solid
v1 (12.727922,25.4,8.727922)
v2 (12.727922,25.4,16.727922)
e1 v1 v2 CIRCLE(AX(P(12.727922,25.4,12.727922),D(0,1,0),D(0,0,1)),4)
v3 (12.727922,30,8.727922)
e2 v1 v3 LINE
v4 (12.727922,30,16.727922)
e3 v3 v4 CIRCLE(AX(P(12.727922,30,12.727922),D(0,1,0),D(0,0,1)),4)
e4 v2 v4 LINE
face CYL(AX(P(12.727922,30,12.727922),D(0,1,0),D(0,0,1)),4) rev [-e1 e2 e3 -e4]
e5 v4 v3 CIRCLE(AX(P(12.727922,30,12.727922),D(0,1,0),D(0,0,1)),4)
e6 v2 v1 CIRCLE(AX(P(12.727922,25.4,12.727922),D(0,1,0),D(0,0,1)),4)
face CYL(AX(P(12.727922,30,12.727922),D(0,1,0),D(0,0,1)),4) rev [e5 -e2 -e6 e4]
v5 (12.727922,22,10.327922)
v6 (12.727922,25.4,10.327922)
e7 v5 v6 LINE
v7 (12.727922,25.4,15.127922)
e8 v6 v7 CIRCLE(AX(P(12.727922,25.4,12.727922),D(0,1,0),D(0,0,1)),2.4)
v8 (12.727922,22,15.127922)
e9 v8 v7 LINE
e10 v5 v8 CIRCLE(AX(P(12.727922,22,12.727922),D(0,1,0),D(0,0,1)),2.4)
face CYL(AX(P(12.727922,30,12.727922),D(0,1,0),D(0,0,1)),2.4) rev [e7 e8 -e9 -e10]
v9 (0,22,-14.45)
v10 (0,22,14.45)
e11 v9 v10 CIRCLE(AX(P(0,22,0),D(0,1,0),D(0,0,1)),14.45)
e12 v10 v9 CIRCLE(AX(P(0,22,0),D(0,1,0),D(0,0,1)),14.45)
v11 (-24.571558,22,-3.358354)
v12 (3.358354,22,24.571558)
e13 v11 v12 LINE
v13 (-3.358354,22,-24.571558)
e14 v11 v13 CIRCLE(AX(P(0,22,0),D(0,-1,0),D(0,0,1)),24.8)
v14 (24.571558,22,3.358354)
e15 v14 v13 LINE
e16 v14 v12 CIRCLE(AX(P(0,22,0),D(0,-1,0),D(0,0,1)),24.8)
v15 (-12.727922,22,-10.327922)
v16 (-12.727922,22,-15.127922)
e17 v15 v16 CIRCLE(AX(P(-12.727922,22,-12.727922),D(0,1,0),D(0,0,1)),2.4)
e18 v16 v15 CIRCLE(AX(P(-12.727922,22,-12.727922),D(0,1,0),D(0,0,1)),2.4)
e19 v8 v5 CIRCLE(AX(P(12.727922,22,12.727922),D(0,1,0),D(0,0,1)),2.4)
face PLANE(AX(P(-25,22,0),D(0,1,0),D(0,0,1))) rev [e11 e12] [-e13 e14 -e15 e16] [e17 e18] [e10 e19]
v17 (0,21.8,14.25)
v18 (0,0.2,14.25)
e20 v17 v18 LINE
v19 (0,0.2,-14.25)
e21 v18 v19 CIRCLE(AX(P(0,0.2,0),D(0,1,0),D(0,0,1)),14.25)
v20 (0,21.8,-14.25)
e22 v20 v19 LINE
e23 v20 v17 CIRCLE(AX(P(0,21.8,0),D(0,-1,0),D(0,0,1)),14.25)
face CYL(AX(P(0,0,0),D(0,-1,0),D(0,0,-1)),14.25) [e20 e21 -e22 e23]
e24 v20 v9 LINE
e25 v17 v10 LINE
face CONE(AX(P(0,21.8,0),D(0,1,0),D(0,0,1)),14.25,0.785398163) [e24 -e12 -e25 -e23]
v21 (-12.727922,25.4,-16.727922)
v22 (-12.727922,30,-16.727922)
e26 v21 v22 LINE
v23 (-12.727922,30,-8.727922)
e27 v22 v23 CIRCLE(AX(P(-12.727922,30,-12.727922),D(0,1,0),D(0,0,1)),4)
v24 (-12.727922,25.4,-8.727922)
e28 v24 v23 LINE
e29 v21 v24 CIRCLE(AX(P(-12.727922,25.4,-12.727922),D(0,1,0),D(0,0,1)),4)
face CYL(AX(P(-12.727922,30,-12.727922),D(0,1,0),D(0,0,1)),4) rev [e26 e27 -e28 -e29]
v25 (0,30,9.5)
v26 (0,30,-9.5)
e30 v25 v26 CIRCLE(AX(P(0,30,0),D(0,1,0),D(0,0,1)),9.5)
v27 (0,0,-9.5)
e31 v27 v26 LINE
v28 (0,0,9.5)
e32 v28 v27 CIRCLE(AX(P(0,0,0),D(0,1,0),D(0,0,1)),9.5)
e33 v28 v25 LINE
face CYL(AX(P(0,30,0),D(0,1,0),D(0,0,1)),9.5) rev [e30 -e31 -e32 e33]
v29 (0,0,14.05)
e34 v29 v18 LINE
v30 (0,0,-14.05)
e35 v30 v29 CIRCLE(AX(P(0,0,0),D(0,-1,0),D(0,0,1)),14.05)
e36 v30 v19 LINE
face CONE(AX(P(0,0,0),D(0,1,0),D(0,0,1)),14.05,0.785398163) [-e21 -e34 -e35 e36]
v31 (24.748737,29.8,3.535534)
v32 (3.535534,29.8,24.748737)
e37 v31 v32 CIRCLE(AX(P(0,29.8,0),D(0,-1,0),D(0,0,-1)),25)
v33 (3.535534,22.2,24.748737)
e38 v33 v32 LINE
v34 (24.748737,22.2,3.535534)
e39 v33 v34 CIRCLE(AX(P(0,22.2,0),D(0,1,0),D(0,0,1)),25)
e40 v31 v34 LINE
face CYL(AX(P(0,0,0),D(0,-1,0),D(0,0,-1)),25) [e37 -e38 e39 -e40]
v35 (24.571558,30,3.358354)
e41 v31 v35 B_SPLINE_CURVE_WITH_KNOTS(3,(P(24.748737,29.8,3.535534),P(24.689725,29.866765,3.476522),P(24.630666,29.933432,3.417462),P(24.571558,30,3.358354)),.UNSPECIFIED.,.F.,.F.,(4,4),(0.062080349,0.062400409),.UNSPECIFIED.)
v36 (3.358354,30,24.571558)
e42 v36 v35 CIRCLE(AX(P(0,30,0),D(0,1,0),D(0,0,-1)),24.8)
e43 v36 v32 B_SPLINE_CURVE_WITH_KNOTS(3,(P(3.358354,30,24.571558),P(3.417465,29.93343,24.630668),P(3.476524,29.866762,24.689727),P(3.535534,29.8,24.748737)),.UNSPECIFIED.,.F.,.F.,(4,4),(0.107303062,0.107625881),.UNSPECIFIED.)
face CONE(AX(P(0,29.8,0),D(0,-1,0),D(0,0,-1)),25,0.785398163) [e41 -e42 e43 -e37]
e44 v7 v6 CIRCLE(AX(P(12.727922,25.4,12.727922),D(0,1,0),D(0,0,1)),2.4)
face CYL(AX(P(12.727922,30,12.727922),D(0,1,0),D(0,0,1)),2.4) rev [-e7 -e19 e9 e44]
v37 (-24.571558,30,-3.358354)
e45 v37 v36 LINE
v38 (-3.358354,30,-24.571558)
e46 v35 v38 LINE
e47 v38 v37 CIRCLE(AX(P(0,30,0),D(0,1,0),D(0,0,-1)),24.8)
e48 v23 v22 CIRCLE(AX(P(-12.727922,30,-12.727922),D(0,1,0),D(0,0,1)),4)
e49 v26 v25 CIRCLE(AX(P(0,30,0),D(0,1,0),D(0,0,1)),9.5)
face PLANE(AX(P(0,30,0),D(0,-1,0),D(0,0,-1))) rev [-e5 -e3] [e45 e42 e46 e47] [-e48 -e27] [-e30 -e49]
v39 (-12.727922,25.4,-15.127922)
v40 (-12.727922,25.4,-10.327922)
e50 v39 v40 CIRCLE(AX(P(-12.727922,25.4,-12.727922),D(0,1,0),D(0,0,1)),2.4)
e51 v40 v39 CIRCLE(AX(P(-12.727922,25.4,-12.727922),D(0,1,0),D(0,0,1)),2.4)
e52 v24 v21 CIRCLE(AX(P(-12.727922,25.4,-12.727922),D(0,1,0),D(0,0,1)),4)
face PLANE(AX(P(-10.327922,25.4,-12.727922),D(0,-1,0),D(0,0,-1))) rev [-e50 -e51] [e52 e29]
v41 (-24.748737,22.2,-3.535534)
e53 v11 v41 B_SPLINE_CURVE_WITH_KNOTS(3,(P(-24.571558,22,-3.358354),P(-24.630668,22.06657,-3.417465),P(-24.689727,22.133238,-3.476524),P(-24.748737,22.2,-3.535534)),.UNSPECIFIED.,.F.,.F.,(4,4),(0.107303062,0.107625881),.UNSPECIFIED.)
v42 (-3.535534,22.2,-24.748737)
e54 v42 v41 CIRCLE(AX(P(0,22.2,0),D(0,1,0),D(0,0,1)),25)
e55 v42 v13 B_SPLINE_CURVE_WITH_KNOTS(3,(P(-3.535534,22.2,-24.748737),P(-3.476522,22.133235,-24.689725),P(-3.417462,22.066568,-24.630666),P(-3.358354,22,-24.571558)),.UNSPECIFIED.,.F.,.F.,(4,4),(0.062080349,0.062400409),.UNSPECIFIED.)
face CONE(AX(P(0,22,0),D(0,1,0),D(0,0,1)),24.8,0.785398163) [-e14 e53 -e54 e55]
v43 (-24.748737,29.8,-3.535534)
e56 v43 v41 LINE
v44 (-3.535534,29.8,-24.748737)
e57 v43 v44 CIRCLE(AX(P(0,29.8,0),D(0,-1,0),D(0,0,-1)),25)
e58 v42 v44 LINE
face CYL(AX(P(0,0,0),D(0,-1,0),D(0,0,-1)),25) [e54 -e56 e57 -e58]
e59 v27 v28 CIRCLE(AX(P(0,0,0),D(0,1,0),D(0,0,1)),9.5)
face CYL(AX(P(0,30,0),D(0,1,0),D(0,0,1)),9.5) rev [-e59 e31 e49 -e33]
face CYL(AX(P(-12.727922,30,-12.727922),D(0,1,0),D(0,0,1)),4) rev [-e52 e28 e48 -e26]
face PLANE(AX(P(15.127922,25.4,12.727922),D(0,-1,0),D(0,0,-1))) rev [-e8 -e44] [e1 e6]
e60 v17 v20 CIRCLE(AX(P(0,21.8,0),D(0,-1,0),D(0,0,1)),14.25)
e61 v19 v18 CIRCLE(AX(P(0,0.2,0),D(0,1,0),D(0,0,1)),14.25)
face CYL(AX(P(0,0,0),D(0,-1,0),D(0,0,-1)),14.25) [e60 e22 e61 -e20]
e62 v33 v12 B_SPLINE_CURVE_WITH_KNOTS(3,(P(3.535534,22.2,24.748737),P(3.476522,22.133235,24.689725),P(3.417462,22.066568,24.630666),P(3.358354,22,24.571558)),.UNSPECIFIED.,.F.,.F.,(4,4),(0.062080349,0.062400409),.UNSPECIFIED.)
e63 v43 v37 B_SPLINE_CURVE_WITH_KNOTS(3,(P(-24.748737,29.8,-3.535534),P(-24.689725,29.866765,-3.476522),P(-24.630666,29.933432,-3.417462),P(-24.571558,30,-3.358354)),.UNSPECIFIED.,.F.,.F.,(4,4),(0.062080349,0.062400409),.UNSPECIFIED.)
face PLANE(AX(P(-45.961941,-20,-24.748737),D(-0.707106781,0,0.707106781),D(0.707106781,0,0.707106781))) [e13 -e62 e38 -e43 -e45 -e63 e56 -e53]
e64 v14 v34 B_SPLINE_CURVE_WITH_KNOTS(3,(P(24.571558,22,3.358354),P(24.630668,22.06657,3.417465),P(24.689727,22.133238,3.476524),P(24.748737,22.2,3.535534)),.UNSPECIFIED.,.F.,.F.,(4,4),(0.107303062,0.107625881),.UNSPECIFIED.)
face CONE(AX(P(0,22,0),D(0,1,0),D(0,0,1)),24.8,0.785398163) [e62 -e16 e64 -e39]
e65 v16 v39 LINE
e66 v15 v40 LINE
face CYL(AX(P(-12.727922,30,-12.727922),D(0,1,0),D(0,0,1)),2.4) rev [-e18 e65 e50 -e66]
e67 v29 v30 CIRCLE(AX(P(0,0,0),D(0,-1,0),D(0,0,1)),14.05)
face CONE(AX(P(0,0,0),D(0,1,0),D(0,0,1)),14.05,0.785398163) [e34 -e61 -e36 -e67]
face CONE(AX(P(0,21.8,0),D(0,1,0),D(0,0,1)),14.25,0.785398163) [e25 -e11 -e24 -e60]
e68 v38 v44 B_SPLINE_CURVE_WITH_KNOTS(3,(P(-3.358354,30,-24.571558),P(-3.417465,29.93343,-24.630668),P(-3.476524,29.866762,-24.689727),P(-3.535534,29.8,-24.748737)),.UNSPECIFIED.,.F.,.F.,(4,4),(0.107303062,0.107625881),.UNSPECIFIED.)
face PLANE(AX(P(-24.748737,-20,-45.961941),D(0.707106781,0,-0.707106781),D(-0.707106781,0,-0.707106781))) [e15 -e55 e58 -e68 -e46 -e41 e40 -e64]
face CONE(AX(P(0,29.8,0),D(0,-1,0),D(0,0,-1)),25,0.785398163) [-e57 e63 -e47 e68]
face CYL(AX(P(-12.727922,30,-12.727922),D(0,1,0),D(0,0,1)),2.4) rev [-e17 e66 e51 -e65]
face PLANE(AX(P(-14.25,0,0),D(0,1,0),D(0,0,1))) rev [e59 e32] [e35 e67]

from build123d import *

# Parameters (mm, degrees)
G1_2_TAPPED_HOLE1_D                               = 19
HOLE_SIZE_BASED_ON_SOCKET_HEAD_CAP_SC_D           = 4.8
HOLE_SIZE_BASED_ON_SOCKET_HEAD_CAP_SC_CBORE_D     = 8
HOLE_SIZE_BASED_ON_SOCKET_HEAD_CAP_SC_CBORE_DEPTH = 4.6
CHAMFER1_SIZE                                     = 0.2
CHAMFER2_SIZE                                     = 0.2
SKETCH7_OUTSIDE_W                                 = 67.362
SKETCH7_OUTSIDE_H                                 = 67.362
CUT_EXTRUDE1_DEPTH                                = 50


with BuildPart() as part:
    # Sketch2 → Revolve1 (revolve)
    with BuildSketch(Plane.XY, mode=Mode.PRIVATE) as revolve1_sk:
        Polygon((0, 30), (-25, 30), (-25, 22), (-14.25, 22), (-14.25, 0), (0, 0), align=None)
    revolve(revolve1_sk.sketch.rotate(Axis((0, 0, 0), (0, 1, 0)), 270), axis=Axis((0, 0, 0), (0, 1, 0)))

    # G1/2 Tapped Hole1 (through all)
    with Locations(Plane.ZX.offset(30)):
        with Locations((0, 0)):
            Hole(G1_2_TAPPED_HOLE1_D / 2)

    # Hole Size (% based on) Socket Head Cap Screw Type 1 (through all)
    with Locations(Plane(origin=(-12.727922061, 30, -12.727922061), x_dir=(0, 0, 1), z_dir=(0, 1, 0))):
        with Locations((0, 0), (25.455844122, 25.455844122)):
            CounterBoreHole(HOLE_SIZE_BASED_ON_SOCKET_HEAD_CAP_SC_D / 2, HOLE_SIZE_BASED_ON_SOCKET_HEAD_CAP_SC_CBORE_D / 2, HOLE_SIZE_BASED_ON_SOCKET_HEAD_CAP_SC_CBORE_DEPTH)

    # Chamfer1
    chamfer1_edges = [part.edges().sort_by_distance(p)[0] for p in [
        (0, 0, 14.25),
        (0, 22, 25),
        (0, 30, 25),
    ]]
    chamfer(chamfer1_edges, length=CHAMFER1_SIZE)

    # Chamfer2
    chamfer2_edges = [part.edges().sort_by_distance(p)[0] for p in [
        (0, 22, 14.25),
    ]]
    chamfer(chamfer2_edges, length=CHAMFER2_SIZE)

    # Sketch7 outside → Cut-Extrude1 (cut)
    with BuildSketch(Plane(origin=(0, 30, 0), x_dir=(1, 0, 0), z_dir=(0, 1, 0))):
        Rectangle(SKETCH7_OUTSIDE_W, SKETCH7_OUTSIDE_H)
        Polygon((-24.748737342, 45.961940777), (45.961940777, -24.748737342), (24.748737342, -45.961940777), (-45.961940777, 24.748737342), align=None, mode=Mode.SUBTRACT)
    extrude(amount=-CUT_EXTRUDE1_DEPTH, mode=Mode.SUBTRACT)


solid = part.part
